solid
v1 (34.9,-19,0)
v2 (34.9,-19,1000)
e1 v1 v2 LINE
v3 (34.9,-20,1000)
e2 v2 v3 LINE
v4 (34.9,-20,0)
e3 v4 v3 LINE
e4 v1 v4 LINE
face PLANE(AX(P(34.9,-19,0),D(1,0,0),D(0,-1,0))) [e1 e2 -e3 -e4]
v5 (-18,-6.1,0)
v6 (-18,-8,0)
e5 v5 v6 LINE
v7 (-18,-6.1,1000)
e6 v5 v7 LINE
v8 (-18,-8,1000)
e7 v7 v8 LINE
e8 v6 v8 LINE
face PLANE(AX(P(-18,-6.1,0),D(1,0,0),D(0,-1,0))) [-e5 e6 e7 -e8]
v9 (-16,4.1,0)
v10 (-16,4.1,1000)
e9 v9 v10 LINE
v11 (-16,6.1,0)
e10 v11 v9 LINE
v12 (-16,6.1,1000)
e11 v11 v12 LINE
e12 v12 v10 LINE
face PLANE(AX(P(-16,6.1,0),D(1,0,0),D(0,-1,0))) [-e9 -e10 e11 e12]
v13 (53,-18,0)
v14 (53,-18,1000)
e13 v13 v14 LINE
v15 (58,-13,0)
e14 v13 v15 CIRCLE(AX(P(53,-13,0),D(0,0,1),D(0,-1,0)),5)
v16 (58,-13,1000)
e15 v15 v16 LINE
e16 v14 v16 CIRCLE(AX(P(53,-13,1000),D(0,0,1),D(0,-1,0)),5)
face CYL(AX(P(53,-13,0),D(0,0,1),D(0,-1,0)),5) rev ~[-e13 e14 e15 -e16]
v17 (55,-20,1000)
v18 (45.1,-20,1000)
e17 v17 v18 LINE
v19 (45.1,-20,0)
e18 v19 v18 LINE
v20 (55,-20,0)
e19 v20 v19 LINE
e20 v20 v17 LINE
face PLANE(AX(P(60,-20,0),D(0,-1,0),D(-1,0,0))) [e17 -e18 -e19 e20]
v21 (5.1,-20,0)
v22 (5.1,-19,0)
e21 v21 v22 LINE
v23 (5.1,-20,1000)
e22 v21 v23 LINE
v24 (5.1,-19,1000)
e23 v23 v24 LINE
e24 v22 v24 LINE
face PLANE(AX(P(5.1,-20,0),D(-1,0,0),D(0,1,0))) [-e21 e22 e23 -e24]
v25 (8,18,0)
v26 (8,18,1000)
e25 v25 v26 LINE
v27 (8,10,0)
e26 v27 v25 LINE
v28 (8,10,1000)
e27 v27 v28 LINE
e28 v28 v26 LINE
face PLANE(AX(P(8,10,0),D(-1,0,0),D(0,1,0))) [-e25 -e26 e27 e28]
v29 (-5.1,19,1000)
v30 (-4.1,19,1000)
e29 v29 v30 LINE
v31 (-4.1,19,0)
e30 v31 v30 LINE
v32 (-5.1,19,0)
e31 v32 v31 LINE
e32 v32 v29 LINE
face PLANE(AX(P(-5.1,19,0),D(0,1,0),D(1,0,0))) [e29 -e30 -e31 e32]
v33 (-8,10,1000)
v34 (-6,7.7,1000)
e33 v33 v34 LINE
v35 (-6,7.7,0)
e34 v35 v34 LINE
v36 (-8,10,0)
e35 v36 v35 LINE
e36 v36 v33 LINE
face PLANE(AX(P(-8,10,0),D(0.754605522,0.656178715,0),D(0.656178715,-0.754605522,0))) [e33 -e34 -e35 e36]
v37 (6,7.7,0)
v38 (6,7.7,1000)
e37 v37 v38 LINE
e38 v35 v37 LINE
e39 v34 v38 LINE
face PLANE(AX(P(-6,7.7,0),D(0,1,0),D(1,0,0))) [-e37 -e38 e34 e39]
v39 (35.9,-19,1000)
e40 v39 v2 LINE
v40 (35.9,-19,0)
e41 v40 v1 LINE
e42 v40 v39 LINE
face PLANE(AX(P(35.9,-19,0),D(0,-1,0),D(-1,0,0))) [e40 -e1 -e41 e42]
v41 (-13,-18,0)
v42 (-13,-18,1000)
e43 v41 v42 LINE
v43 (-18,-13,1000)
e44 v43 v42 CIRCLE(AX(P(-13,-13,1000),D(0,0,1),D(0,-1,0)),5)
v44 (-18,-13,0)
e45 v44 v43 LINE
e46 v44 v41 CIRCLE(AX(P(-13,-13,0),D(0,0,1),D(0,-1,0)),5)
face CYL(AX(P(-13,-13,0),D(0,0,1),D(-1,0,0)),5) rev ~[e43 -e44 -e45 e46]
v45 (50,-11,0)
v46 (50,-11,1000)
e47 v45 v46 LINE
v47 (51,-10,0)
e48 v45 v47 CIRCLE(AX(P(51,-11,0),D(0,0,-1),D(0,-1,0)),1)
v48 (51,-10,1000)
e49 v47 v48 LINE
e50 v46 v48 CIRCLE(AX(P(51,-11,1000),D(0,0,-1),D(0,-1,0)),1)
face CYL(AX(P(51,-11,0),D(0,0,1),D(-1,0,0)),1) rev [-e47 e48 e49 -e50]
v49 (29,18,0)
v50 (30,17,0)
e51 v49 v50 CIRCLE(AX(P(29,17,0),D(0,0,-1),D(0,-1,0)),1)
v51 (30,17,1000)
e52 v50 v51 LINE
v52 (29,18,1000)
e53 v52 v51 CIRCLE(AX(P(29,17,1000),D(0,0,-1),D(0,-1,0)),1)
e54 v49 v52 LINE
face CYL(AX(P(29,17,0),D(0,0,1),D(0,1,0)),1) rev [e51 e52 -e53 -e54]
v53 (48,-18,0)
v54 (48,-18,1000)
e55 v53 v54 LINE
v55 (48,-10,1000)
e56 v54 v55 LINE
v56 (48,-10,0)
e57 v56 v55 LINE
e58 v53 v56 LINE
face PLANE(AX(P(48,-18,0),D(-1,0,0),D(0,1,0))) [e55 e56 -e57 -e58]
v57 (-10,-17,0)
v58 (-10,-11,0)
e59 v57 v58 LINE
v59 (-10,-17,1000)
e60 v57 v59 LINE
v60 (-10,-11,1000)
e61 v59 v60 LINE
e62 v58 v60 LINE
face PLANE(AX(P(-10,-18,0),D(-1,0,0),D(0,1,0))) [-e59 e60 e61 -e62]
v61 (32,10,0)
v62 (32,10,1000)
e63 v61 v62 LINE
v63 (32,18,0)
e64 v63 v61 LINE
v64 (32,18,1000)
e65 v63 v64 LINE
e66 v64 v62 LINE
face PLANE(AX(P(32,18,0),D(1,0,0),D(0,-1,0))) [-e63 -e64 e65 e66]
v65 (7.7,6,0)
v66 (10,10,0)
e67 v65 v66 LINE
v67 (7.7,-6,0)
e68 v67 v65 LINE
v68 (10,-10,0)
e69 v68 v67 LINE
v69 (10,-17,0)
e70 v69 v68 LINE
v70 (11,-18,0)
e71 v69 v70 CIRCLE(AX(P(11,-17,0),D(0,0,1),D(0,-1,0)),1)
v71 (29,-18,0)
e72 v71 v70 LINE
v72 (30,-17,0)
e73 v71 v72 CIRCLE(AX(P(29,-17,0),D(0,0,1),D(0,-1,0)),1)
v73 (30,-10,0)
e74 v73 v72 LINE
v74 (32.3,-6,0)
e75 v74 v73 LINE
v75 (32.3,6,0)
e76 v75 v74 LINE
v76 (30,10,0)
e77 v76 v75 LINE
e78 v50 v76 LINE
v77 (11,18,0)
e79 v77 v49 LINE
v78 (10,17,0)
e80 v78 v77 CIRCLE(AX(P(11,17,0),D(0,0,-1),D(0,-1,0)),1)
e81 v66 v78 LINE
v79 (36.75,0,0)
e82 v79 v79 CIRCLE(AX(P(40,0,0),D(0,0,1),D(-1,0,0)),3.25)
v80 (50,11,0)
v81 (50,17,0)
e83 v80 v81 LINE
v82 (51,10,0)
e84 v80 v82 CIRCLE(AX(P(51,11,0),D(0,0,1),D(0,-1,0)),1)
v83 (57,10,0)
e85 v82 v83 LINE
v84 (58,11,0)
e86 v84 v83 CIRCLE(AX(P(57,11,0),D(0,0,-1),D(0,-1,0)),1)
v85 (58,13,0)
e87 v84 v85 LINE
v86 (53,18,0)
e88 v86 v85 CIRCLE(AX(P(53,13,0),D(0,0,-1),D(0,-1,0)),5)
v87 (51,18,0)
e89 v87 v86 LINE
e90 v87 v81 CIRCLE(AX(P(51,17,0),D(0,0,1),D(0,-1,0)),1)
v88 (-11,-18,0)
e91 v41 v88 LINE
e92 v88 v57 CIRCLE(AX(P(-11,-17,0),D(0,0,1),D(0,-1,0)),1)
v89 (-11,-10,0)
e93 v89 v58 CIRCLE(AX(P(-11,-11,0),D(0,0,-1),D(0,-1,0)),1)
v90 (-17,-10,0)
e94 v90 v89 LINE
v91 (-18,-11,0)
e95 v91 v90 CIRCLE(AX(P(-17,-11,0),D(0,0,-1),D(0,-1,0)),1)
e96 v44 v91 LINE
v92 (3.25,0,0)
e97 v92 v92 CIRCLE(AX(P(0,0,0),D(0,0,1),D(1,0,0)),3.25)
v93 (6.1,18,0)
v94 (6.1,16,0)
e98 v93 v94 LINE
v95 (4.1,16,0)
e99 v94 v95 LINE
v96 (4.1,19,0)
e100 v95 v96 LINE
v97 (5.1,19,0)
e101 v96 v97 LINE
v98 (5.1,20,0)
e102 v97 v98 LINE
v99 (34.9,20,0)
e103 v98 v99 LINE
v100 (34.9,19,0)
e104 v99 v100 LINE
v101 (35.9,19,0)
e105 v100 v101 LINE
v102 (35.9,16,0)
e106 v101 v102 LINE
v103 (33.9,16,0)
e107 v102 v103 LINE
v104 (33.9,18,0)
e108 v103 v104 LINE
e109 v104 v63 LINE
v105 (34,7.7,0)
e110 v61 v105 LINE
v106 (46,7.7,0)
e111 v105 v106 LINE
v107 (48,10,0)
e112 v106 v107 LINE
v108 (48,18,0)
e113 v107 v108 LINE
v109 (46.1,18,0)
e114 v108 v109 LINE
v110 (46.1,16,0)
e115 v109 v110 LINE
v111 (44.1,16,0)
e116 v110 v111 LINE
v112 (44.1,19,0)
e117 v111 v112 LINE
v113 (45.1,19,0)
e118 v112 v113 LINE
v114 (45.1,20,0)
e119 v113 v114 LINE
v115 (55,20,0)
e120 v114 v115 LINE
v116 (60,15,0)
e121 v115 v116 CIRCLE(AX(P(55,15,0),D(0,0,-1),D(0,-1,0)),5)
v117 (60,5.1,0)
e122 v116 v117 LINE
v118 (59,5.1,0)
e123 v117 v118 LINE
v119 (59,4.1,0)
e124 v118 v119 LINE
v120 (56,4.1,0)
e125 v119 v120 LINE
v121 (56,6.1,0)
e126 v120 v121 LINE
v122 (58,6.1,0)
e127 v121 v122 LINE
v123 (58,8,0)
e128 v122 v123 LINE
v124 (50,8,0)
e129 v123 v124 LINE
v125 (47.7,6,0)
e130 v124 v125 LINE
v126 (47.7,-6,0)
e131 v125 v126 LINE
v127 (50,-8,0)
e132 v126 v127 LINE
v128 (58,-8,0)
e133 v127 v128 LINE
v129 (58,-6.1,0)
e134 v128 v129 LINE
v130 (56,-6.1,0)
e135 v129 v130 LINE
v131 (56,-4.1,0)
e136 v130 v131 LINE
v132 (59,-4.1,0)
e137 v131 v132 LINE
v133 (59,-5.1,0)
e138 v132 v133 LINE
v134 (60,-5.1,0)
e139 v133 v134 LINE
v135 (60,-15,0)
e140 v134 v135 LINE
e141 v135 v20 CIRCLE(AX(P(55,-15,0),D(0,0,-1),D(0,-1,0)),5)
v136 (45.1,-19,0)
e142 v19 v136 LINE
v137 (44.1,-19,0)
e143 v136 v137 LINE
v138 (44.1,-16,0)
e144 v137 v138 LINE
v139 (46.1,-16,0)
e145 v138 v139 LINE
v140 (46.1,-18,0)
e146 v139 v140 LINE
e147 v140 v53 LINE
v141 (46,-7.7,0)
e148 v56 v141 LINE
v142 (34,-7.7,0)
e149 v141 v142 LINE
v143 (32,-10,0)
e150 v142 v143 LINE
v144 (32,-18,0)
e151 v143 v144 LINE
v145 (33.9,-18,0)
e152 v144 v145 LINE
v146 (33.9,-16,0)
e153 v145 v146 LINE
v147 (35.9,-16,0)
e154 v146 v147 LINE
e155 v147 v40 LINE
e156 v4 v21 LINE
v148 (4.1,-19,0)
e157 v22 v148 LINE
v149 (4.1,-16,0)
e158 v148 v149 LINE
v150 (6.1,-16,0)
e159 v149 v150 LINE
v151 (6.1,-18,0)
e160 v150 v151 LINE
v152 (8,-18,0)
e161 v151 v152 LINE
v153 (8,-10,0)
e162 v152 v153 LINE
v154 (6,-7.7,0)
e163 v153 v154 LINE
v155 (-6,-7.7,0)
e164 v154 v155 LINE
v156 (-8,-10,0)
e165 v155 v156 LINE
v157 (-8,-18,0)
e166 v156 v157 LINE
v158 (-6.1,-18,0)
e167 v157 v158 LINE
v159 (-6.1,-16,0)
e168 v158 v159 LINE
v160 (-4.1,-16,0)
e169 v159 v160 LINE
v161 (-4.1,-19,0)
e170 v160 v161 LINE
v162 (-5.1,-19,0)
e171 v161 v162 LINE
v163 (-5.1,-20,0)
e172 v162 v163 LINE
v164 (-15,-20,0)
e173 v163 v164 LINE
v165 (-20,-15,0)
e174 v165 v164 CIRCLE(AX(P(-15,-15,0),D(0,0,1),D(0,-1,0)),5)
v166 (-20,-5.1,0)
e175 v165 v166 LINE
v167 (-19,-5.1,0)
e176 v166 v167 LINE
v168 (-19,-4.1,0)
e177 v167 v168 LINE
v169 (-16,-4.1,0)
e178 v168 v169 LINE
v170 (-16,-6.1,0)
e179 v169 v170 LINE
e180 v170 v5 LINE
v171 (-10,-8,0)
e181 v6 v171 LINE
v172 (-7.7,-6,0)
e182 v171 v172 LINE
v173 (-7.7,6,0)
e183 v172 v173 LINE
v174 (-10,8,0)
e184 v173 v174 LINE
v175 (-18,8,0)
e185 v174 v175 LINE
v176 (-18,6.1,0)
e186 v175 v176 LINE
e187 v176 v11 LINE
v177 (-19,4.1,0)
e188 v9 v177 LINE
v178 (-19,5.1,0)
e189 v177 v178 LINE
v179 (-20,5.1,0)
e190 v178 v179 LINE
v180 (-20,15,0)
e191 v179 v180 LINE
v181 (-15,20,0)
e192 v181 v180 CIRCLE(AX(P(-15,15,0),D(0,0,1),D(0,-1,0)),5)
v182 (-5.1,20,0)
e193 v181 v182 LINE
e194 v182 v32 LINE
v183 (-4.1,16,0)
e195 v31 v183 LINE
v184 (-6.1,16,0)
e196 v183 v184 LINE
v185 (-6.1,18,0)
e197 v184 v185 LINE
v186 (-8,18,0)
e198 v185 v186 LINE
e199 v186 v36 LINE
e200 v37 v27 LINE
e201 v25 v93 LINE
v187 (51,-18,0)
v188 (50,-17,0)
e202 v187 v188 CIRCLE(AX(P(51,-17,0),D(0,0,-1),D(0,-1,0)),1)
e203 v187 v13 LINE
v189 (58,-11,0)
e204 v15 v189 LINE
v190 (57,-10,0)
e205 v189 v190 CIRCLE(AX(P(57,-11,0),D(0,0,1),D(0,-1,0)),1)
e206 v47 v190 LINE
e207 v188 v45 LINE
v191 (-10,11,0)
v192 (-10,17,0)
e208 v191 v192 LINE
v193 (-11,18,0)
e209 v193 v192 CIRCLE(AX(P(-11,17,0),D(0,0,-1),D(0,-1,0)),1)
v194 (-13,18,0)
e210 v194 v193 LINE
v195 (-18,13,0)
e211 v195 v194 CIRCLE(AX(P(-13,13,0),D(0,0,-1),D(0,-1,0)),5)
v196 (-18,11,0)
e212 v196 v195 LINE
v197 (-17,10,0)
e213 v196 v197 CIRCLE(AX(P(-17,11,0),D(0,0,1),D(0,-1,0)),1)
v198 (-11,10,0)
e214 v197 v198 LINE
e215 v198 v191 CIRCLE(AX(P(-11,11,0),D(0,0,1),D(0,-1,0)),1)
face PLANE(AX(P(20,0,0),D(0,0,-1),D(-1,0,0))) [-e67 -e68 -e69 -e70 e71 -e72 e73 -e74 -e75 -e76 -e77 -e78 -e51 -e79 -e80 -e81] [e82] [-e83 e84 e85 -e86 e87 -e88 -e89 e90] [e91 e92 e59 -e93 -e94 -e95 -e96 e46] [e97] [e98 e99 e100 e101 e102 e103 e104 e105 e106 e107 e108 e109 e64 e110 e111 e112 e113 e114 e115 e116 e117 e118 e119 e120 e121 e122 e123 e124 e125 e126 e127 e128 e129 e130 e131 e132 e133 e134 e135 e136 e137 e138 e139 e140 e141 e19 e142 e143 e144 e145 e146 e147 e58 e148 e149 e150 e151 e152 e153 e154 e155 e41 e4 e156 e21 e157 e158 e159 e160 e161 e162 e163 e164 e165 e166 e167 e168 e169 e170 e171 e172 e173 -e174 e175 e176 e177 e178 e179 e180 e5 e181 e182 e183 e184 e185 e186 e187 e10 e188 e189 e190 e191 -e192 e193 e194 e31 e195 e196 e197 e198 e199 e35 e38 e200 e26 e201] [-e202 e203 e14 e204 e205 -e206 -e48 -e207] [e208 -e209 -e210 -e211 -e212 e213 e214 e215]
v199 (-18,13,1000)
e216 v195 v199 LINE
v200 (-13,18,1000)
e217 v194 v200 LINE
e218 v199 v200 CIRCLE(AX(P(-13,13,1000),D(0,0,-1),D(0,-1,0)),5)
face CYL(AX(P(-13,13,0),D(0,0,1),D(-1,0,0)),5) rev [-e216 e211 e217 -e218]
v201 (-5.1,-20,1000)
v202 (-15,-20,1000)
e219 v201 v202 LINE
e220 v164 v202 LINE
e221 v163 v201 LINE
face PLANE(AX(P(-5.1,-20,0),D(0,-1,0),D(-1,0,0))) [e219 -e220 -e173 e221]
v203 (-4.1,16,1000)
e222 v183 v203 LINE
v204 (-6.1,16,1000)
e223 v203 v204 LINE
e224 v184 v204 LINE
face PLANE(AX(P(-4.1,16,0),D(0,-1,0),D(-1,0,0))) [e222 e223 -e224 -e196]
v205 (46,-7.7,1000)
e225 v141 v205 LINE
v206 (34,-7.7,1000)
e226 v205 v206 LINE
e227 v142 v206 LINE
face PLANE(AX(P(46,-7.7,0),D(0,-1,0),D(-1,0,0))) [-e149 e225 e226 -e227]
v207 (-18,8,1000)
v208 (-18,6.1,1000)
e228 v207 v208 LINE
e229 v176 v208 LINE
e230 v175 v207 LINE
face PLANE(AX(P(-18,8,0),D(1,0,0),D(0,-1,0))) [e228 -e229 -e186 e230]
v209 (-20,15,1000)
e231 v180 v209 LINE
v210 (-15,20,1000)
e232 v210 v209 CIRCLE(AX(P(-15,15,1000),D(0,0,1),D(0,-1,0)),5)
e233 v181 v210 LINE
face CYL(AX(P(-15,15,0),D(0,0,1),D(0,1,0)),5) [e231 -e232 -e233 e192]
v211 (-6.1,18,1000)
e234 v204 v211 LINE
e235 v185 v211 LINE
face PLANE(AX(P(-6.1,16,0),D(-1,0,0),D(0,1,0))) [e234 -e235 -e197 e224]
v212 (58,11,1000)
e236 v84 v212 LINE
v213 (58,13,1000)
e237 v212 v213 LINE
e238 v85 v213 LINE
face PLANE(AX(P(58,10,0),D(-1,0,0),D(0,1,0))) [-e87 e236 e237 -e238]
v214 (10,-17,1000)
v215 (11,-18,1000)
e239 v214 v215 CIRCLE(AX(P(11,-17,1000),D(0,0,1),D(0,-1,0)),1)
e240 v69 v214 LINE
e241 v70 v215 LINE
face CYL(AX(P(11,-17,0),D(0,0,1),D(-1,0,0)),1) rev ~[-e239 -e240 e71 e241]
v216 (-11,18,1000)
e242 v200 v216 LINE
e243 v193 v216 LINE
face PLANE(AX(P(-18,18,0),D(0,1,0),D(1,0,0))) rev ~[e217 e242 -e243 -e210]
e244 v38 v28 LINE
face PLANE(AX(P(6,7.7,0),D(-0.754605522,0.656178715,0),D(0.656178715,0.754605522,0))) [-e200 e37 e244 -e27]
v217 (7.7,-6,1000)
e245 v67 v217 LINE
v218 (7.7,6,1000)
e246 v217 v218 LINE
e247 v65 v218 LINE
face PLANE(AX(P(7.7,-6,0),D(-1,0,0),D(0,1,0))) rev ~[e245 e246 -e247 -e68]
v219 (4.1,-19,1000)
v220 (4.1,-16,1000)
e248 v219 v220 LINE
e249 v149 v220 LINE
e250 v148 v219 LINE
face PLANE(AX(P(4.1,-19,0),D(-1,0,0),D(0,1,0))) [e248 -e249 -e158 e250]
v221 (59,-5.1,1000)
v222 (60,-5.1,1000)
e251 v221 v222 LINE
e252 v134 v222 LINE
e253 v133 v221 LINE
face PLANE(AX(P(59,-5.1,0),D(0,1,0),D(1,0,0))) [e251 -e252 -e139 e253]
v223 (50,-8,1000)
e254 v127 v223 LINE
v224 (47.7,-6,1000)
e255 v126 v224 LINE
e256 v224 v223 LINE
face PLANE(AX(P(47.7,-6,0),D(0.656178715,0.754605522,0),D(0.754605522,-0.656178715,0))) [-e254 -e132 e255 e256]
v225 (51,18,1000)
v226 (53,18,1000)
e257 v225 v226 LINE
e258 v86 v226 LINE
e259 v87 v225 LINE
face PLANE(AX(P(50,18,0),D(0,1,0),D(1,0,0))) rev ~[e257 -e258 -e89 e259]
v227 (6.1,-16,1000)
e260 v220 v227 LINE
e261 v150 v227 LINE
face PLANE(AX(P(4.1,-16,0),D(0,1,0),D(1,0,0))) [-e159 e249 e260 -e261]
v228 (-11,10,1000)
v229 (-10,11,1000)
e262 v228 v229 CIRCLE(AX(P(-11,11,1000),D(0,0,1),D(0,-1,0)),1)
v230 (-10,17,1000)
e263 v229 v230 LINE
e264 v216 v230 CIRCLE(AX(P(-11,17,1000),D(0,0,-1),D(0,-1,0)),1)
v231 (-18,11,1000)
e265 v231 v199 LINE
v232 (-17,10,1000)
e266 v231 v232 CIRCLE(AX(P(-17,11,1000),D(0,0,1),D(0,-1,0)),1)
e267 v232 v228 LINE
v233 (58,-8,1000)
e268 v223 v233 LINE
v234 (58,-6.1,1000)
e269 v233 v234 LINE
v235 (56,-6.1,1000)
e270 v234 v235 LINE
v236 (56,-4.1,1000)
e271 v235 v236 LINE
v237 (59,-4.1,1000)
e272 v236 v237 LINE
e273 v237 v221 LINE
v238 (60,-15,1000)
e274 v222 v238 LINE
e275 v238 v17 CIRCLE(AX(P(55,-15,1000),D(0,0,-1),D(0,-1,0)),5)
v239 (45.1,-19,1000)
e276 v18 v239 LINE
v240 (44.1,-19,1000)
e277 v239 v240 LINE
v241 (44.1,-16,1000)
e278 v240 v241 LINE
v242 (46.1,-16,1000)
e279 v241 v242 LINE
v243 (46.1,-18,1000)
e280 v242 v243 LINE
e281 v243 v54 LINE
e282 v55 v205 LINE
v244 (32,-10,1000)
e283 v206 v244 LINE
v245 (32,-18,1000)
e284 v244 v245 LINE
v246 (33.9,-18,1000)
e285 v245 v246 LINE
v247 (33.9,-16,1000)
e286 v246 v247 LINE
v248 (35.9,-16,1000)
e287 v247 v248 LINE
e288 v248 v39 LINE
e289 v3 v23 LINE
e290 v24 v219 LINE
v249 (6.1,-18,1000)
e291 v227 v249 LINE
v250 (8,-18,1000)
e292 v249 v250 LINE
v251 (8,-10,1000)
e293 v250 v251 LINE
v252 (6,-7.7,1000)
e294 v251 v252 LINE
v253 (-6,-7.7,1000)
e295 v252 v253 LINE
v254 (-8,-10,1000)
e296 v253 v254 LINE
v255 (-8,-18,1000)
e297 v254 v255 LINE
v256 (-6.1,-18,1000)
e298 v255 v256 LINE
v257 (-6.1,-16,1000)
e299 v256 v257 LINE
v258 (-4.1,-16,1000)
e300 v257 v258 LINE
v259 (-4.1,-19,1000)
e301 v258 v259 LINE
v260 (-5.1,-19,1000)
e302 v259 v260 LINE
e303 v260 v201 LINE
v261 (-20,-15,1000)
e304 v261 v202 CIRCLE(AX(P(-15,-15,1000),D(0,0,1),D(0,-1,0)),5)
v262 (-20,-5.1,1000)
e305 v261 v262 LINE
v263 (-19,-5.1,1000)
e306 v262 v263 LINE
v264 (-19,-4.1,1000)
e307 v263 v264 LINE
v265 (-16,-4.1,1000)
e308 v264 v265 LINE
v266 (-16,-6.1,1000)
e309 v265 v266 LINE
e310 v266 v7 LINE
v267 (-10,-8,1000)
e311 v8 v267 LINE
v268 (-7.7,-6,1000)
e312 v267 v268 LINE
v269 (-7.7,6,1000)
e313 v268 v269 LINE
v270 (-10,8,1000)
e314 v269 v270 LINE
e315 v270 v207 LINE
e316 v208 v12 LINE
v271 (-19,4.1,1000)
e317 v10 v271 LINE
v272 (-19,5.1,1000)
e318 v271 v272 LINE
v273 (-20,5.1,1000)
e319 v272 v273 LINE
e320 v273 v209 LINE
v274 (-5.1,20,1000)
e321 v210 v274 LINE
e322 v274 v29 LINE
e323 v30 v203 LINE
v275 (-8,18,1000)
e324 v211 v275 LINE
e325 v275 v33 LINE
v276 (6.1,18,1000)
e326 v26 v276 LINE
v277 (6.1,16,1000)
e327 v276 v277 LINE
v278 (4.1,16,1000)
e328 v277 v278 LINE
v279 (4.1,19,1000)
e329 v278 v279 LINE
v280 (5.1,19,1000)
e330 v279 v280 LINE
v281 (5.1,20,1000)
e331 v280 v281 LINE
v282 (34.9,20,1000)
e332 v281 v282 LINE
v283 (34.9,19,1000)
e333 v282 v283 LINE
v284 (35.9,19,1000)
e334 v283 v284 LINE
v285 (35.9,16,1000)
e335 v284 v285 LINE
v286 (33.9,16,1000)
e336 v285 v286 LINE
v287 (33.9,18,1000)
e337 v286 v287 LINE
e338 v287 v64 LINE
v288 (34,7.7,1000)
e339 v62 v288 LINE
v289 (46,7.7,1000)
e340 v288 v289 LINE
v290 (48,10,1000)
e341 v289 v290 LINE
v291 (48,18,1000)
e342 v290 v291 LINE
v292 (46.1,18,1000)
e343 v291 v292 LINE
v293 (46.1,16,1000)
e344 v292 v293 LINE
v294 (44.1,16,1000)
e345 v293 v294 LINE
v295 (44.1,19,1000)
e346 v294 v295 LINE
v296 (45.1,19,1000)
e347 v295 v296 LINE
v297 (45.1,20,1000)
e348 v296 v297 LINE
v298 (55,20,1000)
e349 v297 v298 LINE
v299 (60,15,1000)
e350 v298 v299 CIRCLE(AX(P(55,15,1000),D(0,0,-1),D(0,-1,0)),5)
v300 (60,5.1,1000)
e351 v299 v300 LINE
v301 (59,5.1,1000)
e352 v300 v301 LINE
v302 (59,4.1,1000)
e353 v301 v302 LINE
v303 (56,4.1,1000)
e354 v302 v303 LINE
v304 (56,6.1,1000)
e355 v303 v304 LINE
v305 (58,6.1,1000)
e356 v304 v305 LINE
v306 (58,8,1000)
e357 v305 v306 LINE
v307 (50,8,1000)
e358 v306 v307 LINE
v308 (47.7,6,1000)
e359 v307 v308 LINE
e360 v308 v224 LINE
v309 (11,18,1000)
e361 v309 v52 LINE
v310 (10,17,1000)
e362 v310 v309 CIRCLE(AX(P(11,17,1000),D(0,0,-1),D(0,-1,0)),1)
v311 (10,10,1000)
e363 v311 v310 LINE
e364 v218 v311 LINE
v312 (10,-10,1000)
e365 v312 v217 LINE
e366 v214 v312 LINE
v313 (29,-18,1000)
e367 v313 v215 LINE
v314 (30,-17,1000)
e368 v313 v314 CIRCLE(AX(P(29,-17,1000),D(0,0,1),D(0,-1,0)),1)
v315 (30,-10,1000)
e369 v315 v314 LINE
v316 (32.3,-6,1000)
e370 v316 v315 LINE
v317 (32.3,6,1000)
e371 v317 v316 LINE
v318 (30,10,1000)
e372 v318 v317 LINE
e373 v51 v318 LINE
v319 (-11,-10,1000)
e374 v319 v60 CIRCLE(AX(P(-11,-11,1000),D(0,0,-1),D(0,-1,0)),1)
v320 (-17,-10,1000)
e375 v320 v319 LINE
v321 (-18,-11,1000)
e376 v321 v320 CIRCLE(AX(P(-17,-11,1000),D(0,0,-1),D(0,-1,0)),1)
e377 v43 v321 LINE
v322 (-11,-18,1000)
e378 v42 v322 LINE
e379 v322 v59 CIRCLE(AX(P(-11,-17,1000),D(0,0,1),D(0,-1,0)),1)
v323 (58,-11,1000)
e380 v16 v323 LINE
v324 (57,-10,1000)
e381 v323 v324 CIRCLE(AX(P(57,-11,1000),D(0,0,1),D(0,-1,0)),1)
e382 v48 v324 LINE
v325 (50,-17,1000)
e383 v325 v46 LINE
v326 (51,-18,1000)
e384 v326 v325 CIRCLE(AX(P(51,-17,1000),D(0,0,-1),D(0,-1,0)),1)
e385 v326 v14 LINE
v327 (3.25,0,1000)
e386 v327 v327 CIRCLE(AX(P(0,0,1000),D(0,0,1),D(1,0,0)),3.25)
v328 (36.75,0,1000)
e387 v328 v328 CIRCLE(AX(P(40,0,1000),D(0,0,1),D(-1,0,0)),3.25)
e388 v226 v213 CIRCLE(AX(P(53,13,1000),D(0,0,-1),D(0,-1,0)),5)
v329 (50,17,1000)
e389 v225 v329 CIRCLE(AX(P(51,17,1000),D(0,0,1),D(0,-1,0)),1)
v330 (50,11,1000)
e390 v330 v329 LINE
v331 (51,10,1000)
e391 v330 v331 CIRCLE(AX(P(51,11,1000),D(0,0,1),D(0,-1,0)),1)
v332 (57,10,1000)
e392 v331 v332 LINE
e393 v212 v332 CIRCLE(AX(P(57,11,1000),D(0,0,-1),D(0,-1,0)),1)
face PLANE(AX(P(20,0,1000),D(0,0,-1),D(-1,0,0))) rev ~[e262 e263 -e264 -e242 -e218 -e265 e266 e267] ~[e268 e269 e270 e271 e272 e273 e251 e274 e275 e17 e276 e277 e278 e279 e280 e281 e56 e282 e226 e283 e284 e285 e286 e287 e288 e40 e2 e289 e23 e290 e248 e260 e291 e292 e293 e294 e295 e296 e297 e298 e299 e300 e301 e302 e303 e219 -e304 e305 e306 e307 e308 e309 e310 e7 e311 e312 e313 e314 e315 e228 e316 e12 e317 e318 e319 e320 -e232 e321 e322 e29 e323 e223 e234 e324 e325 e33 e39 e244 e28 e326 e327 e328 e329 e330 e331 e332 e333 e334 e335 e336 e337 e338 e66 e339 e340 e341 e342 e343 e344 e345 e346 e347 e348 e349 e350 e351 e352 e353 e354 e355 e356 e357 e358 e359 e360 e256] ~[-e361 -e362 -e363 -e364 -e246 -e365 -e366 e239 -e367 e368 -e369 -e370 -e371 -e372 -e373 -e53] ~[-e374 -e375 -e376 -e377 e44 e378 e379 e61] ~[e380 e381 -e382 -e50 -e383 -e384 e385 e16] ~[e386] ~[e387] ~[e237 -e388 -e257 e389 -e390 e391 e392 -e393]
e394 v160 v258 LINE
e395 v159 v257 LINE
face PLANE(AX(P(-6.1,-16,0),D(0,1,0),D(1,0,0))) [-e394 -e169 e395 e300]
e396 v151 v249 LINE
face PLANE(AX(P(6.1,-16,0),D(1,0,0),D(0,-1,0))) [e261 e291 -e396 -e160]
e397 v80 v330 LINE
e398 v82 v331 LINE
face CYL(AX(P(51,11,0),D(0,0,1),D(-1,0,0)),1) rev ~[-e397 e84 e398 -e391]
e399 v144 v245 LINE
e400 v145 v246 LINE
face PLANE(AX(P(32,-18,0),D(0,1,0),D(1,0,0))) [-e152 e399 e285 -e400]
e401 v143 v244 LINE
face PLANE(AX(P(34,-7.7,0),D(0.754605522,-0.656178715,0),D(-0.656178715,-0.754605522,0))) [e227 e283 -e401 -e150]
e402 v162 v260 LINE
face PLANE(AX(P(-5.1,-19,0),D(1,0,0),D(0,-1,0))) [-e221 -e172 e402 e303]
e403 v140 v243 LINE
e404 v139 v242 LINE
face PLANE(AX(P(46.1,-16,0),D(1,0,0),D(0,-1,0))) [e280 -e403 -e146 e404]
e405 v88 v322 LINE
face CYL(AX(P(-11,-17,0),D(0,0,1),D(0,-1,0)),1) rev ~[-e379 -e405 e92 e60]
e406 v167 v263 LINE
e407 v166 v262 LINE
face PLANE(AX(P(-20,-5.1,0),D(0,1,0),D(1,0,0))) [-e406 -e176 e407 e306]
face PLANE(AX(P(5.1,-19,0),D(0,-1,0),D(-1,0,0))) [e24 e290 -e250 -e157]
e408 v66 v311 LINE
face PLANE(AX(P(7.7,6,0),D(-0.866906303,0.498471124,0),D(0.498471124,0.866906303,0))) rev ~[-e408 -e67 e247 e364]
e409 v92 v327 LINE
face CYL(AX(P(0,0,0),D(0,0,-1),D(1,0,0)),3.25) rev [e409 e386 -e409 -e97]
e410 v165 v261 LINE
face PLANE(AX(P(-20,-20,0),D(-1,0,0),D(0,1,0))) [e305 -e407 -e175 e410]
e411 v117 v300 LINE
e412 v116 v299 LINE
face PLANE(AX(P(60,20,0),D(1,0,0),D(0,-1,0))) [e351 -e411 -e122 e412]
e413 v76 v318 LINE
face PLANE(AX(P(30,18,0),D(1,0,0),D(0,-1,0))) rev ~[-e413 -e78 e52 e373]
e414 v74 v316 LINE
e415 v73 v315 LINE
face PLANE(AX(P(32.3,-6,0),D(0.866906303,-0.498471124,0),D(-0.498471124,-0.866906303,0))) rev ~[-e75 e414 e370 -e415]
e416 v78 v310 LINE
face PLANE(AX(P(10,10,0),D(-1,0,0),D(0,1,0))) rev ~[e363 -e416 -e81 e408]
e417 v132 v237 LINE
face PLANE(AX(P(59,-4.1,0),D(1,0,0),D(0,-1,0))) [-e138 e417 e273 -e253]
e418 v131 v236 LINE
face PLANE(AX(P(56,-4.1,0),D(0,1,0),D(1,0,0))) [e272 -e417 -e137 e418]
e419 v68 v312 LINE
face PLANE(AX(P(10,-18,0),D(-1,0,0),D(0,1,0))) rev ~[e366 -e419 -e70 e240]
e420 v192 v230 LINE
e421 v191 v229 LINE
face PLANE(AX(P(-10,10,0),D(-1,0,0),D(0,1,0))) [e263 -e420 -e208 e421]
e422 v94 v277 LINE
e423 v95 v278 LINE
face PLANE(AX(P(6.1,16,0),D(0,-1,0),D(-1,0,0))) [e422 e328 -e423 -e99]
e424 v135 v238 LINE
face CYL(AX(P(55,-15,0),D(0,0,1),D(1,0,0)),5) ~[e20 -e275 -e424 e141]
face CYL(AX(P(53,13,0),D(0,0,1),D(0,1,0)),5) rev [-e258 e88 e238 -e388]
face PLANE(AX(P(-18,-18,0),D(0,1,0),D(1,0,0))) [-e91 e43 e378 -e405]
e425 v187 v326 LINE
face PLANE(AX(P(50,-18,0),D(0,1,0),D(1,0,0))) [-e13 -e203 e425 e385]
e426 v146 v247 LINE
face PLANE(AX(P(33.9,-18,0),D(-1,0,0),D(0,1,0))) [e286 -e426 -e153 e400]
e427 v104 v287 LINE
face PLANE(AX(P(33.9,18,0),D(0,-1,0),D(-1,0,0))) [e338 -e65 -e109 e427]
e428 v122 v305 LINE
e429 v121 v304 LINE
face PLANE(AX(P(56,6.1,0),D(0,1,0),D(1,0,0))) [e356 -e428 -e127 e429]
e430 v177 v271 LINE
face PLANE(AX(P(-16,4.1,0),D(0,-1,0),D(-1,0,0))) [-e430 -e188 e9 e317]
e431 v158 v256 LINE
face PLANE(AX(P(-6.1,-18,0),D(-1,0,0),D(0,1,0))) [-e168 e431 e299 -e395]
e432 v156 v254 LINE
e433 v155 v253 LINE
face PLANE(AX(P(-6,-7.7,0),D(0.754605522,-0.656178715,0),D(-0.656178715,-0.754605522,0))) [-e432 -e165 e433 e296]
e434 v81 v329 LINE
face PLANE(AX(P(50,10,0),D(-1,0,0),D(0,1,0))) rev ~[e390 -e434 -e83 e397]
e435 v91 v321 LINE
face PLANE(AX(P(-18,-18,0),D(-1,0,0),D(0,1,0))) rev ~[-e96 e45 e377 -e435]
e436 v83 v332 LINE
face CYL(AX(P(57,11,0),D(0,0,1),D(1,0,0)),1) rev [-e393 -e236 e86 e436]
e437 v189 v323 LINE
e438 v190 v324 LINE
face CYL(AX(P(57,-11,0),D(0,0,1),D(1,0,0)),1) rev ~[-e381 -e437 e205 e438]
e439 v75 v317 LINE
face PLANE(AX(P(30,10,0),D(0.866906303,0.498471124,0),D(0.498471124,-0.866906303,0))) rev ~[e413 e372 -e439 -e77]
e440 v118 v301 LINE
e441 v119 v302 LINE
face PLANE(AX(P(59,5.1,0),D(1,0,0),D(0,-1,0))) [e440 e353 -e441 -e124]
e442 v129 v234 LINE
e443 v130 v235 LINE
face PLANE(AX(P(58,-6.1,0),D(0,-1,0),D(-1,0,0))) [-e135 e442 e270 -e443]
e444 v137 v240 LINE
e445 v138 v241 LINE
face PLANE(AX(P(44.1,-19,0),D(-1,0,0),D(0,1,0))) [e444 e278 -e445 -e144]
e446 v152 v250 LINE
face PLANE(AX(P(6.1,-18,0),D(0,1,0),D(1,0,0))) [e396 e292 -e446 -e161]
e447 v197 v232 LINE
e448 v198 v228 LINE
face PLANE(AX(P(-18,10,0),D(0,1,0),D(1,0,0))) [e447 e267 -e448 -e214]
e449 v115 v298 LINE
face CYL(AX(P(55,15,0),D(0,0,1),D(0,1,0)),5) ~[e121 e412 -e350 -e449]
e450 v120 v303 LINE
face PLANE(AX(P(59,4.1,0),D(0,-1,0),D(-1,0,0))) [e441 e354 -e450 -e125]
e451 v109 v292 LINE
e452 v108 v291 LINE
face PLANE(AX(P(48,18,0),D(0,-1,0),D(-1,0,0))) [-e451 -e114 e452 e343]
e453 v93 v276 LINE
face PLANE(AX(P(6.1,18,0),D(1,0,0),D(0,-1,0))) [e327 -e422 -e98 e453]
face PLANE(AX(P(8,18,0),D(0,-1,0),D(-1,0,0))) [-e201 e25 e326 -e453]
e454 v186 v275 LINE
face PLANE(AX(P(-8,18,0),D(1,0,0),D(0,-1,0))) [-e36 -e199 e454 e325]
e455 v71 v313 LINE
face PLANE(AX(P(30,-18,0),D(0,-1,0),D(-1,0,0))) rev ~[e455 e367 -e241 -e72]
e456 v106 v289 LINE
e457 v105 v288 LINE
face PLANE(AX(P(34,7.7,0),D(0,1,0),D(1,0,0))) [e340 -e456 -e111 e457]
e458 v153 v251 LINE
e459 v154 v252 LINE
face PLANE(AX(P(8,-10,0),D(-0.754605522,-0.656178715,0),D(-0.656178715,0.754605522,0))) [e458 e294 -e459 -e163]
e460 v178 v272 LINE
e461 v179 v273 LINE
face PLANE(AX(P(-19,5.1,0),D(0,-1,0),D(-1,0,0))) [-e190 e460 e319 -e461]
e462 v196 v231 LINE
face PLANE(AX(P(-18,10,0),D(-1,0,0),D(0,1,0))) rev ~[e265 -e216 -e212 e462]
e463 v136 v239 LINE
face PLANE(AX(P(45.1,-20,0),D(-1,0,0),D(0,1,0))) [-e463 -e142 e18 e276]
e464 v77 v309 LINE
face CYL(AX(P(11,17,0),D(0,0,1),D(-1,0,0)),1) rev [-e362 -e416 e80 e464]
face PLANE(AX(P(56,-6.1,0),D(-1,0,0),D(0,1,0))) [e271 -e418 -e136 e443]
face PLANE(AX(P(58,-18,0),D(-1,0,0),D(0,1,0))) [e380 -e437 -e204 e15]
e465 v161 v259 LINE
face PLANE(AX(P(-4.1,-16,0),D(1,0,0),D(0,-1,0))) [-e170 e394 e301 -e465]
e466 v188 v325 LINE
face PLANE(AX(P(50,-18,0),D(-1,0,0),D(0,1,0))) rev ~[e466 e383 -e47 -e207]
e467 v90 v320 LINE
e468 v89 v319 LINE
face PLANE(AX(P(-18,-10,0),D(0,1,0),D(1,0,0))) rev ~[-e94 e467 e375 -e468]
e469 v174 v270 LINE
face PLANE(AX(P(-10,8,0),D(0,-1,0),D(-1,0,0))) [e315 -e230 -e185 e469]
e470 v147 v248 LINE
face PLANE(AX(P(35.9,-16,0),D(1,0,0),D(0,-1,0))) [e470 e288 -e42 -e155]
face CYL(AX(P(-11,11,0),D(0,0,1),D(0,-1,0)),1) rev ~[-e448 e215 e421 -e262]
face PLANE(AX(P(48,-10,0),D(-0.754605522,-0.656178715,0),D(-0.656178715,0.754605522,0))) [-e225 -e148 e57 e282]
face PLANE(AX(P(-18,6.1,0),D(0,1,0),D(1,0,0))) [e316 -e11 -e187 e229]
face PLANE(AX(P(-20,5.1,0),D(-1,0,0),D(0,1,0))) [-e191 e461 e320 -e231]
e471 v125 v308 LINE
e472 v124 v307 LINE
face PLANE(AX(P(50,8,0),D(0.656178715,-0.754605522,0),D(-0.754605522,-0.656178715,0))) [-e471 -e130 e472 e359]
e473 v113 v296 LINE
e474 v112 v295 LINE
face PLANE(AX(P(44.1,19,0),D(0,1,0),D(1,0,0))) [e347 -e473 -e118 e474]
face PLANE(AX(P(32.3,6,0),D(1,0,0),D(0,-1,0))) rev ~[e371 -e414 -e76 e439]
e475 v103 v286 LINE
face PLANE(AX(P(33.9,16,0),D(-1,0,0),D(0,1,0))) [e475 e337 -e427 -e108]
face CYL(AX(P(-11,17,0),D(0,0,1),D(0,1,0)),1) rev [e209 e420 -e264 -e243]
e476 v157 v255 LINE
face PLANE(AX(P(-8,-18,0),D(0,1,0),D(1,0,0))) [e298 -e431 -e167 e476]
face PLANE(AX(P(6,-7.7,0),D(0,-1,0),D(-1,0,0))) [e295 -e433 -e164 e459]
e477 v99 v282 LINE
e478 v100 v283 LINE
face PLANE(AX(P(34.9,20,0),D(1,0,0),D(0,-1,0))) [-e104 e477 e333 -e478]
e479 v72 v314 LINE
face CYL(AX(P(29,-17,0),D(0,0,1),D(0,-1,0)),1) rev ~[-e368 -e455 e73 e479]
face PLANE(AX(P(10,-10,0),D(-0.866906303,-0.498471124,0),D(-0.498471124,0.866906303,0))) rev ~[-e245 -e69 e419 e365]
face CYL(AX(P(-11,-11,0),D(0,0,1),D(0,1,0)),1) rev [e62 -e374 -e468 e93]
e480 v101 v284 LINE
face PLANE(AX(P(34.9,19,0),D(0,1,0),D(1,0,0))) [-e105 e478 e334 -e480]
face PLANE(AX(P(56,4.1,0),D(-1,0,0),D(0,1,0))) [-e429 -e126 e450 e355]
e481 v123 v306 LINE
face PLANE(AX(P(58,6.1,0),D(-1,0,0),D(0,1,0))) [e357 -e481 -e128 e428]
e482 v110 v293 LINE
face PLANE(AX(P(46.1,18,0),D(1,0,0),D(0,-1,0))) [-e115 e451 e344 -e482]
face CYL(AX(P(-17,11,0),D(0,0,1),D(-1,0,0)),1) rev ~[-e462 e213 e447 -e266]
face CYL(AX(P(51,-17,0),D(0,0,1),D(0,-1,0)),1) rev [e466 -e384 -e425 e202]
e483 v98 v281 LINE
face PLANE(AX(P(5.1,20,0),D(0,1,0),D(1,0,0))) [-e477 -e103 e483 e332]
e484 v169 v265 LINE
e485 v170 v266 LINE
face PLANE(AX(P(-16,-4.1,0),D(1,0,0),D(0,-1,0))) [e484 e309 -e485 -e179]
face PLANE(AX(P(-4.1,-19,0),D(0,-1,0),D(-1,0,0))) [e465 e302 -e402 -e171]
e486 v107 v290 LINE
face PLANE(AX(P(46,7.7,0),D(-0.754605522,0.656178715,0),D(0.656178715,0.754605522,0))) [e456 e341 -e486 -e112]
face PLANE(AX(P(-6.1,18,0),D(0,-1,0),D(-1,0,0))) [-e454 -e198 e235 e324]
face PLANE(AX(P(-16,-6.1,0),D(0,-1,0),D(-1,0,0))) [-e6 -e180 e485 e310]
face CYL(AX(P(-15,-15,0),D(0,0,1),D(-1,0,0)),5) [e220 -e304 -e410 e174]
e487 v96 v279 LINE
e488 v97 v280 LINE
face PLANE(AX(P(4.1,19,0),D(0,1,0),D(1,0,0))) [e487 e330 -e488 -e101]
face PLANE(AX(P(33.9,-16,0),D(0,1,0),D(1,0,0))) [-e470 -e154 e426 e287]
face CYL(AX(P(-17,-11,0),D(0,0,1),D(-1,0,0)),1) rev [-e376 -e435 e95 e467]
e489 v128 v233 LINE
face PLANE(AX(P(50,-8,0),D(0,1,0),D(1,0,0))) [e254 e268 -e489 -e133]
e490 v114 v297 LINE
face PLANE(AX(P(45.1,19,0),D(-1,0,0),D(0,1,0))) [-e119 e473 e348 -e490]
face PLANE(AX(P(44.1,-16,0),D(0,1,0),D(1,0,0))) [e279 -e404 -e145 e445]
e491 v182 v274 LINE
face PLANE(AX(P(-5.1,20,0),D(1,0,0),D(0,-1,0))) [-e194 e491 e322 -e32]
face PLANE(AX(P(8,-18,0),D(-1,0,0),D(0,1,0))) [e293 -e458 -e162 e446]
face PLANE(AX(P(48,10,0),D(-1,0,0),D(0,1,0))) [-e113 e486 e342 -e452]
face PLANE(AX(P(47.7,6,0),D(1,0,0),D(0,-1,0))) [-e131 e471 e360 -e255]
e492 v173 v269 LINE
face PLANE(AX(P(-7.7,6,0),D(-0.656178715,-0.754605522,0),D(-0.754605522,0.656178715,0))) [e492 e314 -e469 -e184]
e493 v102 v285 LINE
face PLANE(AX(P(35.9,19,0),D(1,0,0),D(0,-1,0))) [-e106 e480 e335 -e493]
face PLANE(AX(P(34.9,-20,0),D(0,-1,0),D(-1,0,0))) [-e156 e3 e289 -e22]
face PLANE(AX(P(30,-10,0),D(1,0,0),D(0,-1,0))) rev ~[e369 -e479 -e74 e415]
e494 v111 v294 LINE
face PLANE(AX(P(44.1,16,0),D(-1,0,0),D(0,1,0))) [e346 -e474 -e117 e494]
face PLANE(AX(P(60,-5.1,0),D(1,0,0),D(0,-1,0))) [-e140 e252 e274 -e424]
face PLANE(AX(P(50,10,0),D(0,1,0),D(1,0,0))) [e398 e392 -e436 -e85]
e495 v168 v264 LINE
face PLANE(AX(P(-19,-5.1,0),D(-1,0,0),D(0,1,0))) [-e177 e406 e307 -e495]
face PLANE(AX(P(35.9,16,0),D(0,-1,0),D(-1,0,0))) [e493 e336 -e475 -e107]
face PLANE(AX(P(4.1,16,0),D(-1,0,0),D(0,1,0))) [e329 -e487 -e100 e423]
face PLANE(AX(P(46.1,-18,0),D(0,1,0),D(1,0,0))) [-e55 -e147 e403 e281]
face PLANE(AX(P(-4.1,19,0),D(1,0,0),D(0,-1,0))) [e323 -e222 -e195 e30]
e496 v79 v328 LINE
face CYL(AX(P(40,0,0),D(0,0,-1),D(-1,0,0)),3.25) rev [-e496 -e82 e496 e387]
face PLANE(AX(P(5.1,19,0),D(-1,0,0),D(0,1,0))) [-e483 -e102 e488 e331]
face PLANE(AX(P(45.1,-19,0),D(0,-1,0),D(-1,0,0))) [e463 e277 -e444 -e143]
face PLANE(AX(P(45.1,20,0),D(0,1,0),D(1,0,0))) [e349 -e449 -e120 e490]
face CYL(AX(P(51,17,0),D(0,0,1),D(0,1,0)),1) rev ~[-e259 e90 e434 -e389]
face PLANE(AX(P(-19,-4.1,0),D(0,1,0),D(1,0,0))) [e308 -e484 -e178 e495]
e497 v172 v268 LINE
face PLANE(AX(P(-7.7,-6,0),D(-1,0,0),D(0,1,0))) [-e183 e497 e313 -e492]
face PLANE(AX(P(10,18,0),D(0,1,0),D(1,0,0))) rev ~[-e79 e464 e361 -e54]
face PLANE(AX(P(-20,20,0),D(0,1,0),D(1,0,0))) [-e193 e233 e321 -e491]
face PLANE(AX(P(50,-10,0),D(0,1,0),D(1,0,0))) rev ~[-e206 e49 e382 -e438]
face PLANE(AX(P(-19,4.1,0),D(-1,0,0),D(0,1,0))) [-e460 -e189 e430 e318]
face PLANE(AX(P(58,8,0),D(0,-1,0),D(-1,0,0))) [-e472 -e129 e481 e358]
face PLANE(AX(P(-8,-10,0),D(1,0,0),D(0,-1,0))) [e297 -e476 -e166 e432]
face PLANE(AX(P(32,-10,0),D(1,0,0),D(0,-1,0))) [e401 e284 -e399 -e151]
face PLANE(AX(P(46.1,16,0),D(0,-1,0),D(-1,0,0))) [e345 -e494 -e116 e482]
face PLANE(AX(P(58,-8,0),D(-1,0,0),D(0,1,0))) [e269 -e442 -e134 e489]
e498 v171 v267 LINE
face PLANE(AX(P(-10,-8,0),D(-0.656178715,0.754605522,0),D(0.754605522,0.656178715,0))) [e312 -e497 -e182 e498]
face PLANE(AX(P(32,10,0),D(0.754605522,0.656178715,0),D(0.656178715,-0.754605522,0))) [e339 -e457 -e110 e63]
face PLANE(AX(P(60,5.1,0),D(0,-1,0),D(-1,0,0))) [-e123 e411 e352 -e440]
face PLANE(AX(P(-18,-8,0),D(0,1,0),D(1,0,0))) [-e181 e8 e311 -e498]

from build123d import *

# Parameters (mm, degrees)
SKETCH_1_R      = 3.25
SKETCH_1_W      = 8
SKETCH_1_H      = 8
EXTRUDE_1_DEPTH = 1000
FILLET_1_R      = 5
FILLET_2_R      = 1


with BuildPart() as part:
    # 草图1 → 拉伸1 (new body)
    with BuildSketch(Plane.XY):
        Polygon((-5.1, 20), (-5.1, 19), (-4.1, 19), (-4.1, 16), (-6.1, 16), (-6.1, 18), (-8, 18), (-8, 10), (-6, 7.7), (6, 7.7), (8, 10), (8, 18), (6.1, 18), (6.1, 16), (4.1, 16), (4.1, 19), (5.1, 19), (5.1, 20), (34.9, 20), (34.9, 19), (35.9, 19), (35.9, 16), (33.9, 16), (33.9, 18), (32, 18), (32, 10), (34, 7.7), (46, 7.7), (48, 10), (48, 18), (46.1, 18), (46.1, 16), (44.1, 16), (44.1, 19), (45.1, 19), (45.1, 20), (60, 20), (60, 5.1), (59, 5.1), (59, 4.1), (56, 4.1), (56, 6.1), (58, 6.1), (58, 8), (50, 8), (47.7, 6), (47.7, -6), (50, -8), (58, -8), (58, -6.1), (56, -6.1), (56, -4.1), (59, -4.1), (59, -5.1), (60, -5.1), (60, -20), (45.1, -20), (45.1, -19), (44.1, -19), (44.1, -16), (46.1, -16), (46.1, -18), (48, -18), (48, -10), (46, -7.7), (34, -7.7), (32, -10), (32, -18), (33.9, -18), (33.9, -16), (35.9, -16), (35.9, -19), (34.9, -19), (34.9, -20), (5.1, -20), (5.1, -19), (4.1, -19), (4.1, -16), (6.1, -16), (6.1, -18), (8, -18), (8, -10), (6, -7.7), (-6, -7.7), (-8, -10), (-8, -18), (-6.1, -18), (-6.1, -16), (-4.1, -16), (-4.1, -19), (-5.1, -19), (-5.1, -20), (-20, -20), (-20, -5.1), (-19, -5.1), (-19, -4.1), (-16, -4.1), (-16, -6.1), (-18, -6.1), (-18, -8), (-10, -8), (-7.7, -6), (-7.7, 6), (-10, 8), (-18, 8), (-18, 6.1), (-16, 6.1), (-16, 4.1), (-19, 4.1), (-19, 5.1), (-20, 5.1), (-20, 20), align=None)
        Circle(SKETCH_1_R, mode=Mode.SUBTRACT)
        with Locations(Location((40, 0, 0), (0, 0, 180))):
            Circle(SKETCH_1_R, mode=Mode.SUBTRACT)
        Polygon((7.7, 6), (10, 10), (10, 18), (30, 18), (30, 10), (32.3, 6), (32.3, -6), (30, -10), (30, -18), (10, -18), (10, -10), (7.7, -6), align=None, mode=Mode.SUBTRACT)
        with Locations((-14, 14)):
            Rectangle(SKETCH_1_W, SKETCH_1_H, mode=Mode.SUBTRACT)
        with Locations((-14, -14)):
            Rectangle(SKETCH_1_W, SKETCH_1_H, mode=Mode.SUBTRACT)
        with Locations((54, -14)):
            Rectangle(SKETCH_1_W, SKETCH_1_H, mode=Mode.SUBTRACT)
        with Locations((54, 14)):
            Rectangle(SKETCH_1_W, SKETCH_1_H, mode=Mode.SUBTRACT)
    extrude(amount=EXTRUDE_1_DEPTH)

    # 圆角1
    fillet_1_edges = [part.edges().sort_by_distance(p)[0] for p in [
        (-20, 20, 500),
        (60, 20, 500),
        (60, -20, 500),
        (-20, -20, 500),
        (-18, 18, 500),
        (-18, -18, 500),
        (58, -18, 500),
        (58, 18, 500),
    ]]
    fillet(fillet_1_edges, radius=FILLET_1_R)

    # 圆角2
    fillet_2_edges = [part.edges().sort_by_distance(p)[0] for p in [
        (10, -18, 500),
        (30, -18, 500),
        (30, 18, 500),
        (10, 18, 500),
        (-18, 10, 500),
        (-10, 10, 500),
        (-10, 18, 500),
        (-10, -18, 500),
        (-10, -10, 500),
        (-18, -10, 500),
        (58, -10, 500),
        (50, -10, 500),
        (50, -18, 500),
        (50, 18, 500),
        (50, 10, 500),
        (58, 10, 500),
    ]]
    fillet(fillet_2_edges, radius=FILLET_2_R)


solid = part.part
